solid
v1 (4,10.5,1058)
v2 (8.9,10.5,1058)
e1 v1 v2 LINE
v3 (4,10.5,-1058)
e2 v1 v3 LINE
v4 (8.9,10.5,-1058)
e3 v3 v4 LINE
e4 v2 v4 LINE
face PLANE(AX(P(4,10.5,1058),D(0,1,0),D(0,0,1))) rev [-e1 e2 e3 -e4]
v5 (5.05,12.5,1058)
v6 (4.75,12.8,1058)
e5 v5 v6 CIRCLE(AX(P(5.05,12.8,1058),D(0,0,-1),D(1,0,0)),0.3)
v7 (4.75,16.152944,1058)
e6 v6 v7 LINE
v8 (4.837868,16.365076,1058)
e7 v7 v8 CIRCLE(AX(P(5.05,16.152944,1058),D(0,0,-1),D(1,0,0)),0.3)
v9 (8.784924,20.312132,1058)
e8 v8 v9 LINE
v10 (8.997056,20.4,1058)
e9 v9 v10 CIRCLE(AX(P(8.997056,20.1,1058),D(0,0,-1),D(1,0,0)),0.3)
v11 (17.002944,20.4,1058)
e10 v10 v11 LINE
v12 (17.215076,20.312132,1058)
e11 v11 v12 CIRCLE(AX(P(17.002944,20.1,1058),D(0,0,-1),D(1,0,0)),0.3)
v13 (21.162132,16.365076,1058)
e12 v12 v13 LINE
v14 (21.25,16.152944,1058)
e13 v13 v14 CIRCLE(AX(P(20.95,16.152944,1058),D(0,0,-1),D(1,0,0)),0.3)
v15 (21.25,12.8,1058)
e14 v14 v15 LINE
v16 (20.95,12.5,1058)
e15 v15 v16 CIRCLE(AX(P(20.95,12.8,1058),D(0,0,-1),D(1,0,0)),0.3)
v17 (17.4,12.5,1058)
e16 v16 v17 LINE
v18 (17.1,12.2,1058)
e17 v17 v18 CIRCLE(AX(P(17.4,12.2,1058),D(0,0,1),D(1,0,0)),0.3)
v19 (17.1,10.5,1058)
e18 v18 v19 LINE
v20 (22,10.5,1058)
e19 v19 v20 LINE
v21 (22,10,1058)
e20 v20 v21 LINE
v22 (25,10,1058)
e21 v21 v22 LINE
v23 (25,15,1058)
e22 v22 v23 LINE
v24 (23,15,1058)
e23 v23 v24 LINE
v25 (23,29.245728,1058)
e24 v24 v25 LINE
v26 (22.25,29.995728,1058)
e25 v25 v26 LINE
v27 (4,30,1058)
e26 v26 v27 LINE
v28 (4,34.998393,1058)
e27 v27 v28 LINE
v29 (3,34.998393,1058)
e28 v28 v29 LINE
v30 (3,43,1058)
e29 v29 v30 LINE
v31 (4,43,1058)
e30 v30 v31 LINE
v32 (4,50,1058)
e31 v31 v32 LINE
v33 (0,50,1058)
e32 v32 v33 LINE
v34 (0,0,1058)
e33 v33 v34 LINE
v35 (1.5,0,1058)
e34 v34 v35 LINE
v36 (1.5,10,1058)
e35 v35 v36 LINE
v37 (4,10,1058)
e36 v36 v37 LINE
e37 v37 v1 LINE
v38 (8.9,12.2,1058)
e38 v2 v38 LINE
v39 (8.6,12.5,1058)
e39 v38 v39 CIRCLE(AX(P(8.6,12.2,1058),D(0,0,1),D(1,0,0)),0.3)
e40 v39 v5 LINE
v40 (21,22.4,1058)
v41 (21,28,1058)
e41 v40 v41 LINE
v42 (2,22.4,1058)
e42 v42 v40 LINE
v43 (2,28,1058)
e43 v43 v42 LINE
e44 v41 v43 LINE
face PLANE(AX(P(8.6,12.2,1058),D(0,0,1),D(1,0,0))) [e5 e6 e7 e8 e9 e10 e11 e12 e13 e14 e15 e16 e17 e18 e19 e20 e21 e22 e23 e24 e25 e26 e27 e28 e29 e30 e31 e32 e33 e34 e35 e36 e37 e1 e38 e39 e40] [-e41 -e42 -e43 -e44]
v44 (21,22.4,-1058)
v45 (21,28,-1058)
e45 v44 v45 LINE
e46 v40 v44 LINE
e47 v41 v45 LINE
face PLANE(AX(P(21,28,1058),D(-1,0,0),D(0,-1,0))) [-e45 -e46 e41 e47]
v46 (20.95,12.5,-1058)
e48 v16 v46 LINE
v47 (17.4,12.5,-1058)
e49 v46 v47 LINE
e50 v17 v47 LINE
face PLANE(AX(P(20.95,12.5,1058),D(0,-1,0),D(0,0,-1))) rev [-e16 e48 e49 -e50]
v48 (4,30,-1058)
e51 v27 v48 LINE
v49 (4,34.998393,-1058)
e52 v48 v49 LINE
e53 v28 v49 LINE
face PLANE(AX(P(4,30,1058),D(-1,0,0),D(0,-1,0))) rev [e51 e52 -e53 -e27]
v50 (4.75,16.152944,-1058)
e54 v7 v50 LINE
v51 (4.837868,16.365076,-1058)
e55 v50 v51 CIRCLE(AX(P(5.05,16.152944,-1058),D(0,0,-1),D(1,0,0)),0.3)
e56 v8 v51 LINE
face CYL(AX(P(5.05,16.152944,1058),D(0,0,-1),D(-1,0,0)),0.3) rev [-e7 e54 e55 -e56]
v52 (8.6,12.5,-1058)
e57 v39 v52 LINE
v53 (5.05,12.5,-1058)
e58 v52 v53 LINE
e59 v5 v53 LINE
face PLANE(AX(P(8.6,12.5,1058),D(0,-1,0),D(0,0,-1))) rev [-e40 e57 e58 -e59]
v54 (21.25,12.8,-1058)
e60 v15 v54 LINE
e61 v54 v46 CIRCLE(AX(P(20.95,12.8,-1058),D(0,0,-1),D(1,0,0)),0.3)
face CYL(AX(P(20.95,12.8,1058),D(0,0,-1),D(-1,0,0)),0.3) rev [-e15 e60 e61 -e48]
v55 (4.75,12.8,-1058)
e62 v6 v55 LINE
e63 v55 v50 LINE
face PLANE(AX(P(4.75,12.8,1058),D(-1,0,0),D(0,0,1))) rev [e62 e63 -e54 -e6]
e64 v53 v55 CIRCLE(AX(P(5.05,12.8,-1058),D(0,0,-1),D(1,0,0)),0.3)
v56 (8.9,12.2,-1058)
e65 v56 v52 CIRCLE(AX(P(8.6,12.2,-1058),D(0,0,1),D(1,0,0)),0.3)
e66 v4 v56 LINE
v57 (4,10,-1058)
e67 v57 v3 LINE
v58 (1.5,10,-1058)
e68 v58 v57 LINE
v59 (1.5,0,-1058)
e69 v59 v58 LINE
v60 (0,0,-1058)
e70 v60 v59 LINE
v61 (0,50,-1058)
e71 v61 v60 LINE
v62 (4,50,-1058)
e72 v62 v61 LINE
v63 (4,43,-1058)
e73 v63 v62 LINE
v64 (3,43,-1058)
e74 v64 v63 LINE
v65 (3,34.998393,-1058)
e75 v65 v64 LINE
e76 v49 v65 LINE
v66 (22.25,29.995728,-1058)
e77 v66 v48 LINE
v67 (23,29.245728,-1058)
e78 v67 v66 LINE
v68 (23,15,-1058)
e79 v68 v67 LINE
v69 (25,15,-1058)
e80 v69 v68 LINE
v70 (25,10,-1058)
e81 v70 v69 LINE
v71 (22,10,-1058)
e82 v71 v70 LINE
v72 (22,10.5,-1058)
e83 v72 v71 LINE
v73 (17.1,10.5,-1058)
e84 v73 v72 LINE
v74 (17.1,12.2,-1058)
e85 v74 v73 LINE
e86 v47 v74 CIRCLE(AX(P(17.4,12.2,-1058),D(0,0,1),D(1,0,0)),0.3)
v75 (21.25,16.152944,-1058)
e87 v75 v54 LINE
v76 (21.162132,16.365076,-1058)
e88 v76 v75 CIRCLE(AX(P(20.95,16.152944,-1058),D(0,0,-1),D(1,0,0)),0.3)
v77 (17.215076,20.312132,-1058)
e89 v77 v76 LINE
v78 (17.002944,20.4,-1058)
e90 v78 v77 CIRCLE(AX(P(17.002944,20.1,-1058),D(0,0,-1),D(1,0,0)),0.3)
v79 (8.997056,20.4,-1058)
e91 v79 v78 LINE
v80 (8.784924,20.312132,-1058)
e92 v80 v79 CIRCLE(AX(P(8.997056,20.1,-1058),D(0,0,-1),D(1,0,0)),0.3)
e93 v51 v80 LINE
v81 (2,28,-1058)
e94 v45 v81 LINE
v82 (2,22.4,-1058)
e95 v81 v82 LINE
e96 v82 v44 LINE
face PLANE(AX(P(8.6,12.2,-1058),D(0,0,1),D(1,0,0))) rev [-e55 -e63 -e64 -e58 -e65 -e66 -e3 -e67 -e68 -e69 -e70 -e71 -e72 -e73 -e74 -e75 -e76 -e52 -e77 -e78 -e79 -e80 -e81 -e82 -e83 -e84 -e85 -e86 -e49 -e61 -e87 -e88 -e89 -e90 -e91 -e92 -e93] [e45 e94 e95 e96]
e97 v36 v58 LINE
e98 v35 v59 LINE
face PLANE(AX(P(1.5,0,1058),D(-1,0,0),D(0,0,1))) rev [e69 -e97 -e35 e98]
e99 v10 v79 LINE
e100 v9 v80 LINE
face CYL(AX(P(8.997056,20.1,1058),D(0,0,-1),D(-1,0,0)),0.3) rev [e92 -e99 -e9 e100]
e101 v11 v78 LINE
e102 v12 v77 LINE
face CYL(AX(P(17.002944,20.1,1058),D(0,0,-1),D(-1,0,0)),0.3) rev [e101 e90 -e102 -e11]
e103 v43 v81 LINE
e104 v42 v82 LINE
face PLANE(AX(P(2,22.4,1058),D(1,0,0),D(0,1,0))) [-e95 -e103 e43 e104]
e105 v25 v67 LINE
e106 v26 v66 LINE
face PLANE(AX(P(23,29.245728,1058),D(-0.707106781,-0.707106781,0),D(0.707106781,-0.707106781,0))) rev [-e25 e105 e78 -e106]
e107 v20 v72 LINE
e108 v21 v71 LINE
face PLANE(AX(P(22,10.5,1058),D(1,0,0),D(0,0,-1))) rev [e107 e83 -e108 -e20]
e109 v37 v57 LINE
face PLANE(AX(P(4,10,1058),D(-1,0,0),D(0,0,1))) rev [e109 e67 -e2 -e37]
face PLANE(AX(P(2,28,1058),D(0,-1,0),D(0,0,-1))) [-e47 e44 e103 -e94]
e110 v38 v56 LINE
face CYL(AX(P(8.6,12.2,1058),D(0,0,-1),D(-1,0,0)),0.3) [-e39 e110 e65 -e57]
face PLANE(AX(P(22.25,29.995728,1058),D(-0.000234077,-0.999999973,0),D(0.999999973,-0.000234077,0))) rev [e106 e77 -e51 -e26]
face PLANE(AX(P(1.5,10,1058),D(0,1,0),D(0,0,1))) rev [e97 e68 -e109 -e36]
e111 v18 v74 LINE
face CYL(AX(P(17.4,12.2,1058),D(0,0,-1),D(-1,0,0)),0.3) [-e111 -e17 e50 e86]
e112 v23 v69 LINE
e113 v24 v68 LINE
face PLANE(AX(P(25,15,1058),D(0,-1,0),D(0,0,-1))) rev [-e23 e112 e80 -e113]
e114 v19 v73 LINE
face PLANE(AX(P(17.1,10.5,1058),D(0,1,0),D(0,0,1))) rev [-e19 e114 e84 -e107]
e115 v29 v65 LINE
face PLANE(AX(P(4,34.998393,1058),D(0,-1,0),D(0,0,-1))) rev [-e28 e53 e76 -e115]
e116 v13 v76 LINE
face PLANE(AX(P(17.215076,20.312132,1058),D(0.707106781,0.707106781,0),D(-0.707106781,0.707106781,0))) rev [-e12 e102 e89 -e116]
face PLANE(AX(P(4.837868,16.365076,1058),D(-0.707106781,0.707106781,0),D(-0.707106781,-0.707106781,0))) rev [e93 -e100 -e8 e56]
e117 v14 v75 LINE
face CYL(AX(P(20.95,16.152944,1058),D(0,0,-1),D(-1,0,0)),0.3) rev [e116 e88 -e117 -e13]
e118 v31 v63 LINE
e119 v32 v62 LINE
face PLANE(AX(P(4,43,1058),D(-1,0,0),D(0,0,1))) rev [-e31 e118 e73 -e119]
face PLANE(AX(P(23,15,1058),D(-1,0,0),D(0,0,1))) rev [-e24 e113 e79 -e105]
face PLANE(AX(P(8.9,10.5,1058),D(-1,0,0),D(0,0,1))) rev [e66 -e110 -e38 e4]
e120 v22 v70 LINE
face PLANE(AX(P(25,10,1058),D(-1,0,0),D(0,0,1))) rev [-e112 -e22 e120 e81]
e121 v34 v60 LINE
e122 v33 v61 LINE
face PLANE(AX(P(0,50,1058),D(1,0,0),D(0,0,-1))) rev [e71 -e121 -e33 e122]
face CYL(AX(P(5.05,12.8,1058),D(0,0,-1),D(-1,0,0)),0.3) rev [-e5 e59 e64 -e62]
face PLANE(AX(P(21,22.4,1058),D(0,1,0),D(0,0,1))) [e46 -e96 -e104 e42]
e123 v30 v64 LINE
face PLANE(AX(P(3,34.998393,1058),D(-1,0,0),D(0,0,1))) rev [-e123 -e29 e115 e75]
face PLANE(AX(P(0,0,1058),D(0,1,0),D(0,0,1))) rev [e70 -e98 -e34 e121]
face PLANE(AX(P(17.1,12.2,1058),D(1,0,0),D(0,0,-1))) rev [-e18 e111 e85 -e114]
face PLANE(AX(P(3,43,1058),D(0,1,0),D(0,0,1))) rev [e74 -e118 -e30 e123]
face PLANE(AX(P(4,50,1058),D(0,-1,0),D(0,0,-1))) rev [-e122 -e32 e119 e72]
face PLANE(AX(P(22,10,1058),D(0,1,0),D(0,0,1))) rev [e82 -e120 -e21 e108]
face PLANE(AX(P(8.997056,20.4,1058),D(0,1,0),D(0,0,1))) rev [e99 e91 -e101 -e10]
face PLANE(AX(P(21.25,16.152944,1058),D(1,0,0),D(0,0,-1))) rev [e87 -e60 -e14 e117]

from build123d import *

# Parameters (mm, degrees)
SKETCH_2_W      = 19
SKETCH_2_H      = 5.6
EXTRUDE_1_DEPTH = 1058


with BuildPart() as part:
    # 草图2 → 凸台-拉伸1 (new, symmetric)
    with BuildSketch(Plane.XY):
        with BuildLine():
            Line((1.5, 10), (4, 10))
            Line((4, 10), (4, 10.5))
            Line((4, 10.5), (8.9, 10.5))
            Line((8.9, 10.5), (8.9, 12.2))
            ThreePointArc((8.9, 12.2), (8.812132034, 12.412132034), (8.6, 12.5))
            Line((8.6, 12.5), (5.05, 12.5))
            ThreePointArc((5.05, 12.5), (4.837867966, 12.587867966), (4.75, 12.8))
            Line((4.75, 12.8), (4.75, 16.152943725))
            ThreePointArc((4.75, 16.152943725), (4.77283614, 16.267748755), (4.837867966, 16.36507576))
            Line((4.837867966, 16.36507576), (8.78492424, 20.312132034))
            ThreePointArc((8.78492424, 20.312132034), (8.882251245, 20.37716386), (8.997056275, 20.4))
            Line((8.997056275, 20.4), (17.002943725, 20.4))
            ThreePointArc((17.002943725, 20.4), (17.117748755, 20.37716386), (17.21507576, 20.312132034))
            Line((17.21507576, 20.312132034), (21.162132034, 16.36507576))
            ThreePointArc((21.162132034, 16.36507576), (21.22716386, 16.267748755), (21.25, 16.152943725))
            Line((21.25, 16.152943725), (21.25, 12.8))
            ThreePointArc((21.25, 12.8), (21.162132034, 12.587867966), (20.95, 12.5))
            Line((20.95, 12.5), (17.4, 12.5))
            ThreePointArc((17.4, 12.5), (17.187867966, 12.412132034), (17.1, 12.2))
            Line((17.1, 12.2), (17.1, 10.5))
            Line((17.1, 10.5), (22, 10.5))
            Line((22, 10.5), (22, 10))
            Line((22, 10), (25, 10))
            Line((25, 10), (25, 15))
            Line((25, 15), (23, 15))
            Line((23, 15), (23, 29.24572809))
            Line((23, 29.24572809), (22.25, 29.99572809))
            Line((22.25, 29.99572809), (4, 30))
            Line((4, 30), (4, 34.998393128))
            Line((4, 34.998393128), (3, 34.998393128))
            Line((3, 34.998393128), (3, 43))
            Line((3, 43), (4, 43))
            Line((4, 43), (4, 50))
            Line((4, 50), (0, 50))
            Line((0, 50), (0, 0))
            Line((0, 0), (1.5, 0))
            Line((1.5, 0), (1.5, 10))
        make_face()
        with Locations((11.5, 25.2)):
            Rectangle(SKETCH_2_W, SKETCH_2_H, mode=Mode.SUBTRACT)
    extrude(amount=EXTRUDE_1_DEPTH, both=True)


solid = part.part
